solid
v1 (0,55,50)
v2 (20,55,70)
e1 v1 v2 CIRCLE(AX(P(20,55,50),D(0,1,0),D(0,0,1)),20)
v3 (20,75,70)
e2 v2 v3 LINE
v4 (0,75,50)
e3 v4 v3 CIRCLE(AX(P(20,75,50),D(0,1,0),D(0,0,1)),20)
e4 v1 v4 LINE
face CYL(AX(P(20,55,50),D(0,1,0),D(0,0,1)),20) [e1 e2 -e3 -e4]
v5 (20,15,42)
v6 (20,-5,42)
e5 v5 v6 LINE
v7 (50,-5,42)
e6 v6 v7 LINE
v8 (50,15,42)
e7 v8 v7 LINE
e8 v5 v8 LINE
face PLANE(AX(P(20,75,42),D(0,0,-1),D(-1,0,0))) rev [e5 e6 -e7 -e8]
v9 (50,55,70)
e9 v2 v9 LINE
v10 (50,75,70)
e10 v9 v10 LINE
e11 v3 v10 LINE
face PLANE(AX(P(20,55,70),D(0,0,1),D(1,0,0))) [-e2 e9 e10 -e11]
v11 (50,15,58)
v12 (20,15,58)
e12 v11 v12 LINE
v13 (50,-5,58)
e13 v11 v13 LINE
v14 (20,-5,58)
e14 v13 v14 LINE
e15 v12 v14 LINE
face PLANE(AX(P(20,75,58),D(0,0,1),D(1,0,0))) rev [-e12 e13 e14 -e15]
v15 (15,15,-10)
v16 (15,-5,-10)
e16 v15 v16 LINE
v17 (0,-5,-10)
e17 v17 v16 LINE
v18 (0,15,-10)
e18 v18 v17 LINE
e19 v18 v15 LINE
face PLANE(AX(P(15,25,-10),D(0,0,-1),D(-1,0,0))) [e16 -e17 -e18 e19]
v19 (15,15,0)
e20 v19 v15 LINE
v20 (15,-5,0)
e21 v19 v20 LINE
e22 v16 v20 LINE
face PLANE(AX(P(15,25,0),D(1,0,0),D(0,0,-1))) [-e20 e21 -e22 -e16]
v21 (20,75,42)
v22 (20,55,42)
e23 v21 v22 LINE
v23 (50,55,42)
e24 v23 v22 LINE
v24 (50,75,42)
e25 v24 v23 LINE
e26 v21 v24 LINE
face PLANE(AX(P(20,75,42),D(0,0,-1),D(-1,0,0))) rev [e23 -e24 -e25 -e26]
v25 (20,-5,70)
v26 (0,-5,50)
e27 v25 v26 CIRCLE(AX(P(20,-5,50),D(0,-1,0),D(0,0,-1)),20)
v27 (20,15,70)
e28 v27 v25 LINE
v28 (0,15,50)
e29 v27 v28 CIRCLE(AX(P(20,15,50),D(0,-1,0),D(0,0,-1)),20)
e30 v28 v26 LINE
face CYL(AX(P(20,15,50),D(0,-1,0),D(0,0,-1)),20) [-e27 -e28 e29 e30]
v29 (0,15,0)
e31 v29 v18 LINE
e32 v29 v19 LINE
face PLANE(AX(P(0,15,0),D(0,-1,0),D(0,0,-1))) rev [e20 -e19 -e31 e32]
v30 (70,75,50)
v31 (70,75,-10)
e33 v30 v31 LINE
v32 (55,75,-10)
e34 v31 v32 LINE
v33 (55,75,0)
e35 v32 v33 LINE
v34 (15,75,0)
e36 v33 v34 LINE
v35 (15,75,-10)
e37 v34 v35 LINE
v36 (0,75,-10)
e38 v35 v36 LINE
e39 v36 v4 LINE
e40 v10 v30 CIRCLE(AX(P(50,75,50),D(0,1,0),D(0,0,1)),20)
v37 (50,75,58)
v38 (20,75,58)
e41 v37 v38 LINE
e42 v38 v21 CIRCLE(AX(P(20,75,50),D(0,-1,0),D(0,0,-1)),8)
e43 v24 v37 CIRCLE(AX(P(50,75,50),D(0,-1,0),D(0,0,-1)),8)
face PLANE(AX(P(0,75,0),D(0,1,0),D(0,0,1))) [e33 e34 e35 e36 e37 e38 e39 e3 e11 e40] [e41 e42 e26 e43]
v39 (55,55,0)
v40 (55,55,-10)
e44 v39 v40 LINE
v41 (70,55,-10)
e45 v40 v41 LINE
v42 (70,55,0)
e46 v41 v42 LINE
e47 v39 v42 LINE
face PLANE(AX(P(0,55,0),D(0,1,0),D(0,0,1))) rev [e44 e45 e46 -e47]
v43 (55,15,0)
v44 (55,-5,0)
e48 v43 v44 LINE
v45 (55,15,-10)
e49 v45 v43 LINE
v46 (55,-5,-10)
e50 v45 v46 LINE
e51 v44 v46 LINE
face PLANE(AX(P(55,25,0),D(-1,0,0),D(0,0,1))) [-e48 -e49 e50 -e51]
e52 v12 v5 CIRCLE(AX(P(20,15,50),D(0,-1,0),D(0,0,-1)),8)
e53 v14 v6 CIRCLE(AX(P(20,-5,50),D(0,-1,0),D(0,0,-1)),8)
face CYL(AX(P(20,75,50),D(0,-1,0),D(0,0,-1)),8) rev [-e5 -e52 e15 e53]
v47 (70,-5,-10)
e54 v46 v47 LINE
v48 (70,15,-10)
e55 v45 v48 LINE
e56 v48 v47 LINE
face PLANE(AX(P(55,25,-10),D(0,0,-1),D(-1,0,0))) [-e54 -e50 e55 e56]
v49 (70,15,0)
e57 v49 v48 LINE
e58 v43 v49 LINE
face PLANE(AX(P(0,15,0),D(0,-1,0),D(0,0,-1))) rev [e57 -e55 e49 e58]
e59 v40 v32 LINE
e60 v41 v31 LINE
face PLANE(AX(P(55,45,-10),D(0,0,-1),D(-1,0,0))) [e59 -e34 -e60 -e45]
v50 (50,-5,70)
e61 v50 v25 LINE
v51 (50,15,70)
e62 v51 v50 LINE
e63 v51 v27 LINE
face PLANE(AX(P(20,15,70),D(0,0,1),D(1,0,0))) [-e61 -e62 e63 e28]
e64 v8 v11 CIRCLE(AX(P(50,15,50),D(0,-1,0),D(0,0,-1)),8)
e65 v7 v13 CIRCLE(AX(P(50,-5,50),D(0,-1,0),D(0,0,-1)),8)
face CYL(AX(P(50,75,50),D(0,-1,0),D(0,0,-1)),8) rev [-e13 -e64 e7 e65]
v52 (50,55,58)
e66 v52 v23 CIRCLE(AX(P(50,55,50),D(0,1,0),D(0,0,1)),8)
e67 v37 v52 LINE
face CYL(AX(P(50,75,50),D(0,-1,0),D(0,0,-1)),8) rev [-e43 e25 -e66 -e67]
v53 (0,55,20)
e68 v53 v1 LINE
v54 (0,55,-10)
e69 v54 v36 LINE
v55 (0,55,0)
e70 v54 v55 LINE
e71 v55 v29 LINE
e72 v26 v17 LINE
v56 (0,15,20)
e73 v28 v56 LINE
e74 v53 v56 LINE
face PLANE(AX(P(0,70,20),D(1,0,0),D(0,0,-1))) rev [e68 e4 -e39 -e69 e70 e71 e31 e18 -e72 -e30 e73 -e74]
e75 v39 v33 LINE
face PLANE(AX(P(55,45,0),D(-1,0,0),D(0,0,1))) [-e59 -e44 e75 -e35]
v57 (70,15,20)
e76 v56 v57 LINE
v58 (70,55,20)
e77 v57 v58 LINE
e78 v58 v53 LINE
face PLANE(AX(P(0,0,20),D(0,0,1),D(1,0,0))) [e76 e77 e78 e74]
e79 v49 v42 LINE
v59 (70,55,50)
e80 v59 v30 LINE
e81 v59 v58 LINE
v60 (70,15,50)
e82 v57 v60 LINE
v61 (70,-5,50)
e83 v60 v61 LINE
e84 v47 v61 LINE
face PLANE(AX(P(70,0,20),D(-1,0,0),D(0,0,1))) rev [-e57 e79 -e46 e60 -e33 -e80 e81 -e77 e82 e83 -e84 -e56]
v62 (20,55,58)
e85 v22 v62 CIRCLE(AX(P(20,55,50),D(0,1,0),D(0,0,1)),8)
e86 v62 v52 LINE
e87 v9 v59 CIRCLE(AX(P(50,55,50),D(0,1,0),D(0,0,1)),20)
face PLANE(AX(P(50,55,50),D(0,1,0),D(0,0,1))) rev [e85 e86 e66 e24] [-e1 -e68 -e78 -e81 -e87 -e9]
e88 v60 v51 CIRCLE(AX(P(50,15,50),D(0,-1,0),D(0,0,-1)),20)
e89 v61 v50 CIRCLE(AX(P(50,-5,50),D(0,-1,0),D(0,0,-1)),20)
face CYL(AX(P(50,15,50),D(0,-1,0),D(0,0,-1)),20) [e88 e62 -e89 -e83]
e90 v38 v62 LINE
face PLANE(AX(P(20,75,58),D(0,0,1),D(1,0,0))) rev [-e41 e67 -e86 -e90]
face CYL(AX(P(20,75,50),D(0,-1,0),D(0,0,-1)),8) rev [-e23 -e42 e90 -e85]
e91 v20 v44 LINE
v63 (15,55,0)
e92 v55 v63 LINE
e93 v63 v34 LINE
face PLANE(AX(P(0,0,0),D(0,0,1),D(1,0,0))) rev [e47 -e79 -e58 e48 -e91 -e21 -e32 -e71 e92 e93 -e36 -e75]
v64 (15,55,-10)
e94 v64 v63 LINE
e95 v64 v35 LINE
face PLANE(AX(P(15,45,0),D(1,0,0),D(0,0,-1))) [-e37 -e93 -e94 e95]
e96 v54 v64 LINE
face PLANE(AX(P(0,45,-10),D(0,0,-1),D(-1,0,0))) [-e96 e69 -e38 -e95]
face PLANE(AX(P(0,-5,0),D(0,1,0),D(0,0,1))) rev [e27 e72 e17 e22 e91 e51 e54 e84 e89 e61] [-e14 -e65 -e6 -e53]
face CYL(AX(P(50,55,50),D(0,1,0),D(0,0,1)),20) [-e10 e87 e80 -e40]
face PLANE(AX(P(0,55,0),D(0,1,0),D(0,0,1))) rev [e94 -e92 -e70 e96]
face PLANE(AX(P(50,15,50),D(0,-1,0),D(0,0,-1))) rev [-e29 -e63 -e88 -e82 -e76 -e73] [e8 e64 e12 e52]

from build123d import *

# Parameters (mm, degrees)
BASE_PLATE_SKETCH_W          = 70
BASE_PLATE_SKETCH_H          = 70
BASE_PLATE_70X70_DEPTH       = 20
WEB_BLOCK_SKETCH_W           = 15
WEB_BLOCK_SKETCH_H           = 10
WEB_BLOCK_DEPTH              = 25
SIDE_BLOCK_A_SKETCH_W        = 15
SIDE_BLOCK_A_SKETCH_H        = 10
SIDE_BLOCK_A_DEPTH           = 25
SIDE_BLOCK_B_SKETCH_W        = 15
SIDE_BLOCK_B_SKETCH_H        = 10
SIDE_BLOCK_B_DEPTH           = 25
POCKET_CUT_A_SKETCH_W        = 10
POCKET_CUT_A_SKETCH_H        = 10
POCKET_CUT_A_DEPTH           = 70
POCKET_CUT_B_SKETCH_W        = 10
POCKET_CUT_B_SKETCH_H        = 10
POCKET_CUT_B_DEPTH           = 70
FLANGE_A_5MM_DEPTH           = 5
FLANGE_B_5MM_DEPTH           = 5
ROUNDED_TAB_A_DEPTH          = 20
ROUNDED_START                = -20
ROUNDED_TAB_B_DEPTH          = 20
TAB_SLOTS_8X30_THROUGH_DEPTH = 80


with BuildPart() as part:
    # Base Plate Sketch → Base Plate 70x70 (new body)
    with BuildSketch(Plane.XY):
        with Locations((35, 35)):
            Rectangle(BASE_PLATE_SKETCH_W, BASE_PLATE_SKETCH_H)
    extrude(amount=BASE_PLATE_70X70_DEPTH)

    # Web Block Sketch → Web Block (add)
    with BuildSketch(Plane.XZ):
        with Locations((7.5, -5)):
            Rectangle(WEB_BLOCK_SKETCH_W, WEB_BLOCK_SKETCH_H)
        with Locations((62.5, -5)):
            Rectangle(WEB_BLOCK_SKETCH_W, WEB_BLOCK_SKETCH_H)
    extrude(amount=-WEB_BLOCK_DEPTH)

    # Side Block A Sketch → Side Block A (add)
    with BuildSketch(Plane(origin=(0, 70, 0), x_dir=(1, 0, 0), z_dir=(0, 1, 0))):
        with Locations((7.5, 5)):
            Rectangle(SIDE_BLOCK_A_SKETCH_W, SIDE_BLOCK_A_SKETCH_H)
    extrude(amount=-SIDE_BLOCK_A_DEPTH)

    # Side Block B Sketch → Side Block B (add)
    with BuildSketch(Plane(origin=(0, 70, 0), x_dir=(1, 0, 0), z_dir=(0, 1, 0))):
        with Locations((62.5, 5)):
            Rectangle(SIDE_BLOCK_B_SKETCH_W, SIDE_BLOCK_B_SKETCH_H)
    extrude(amount=-SIDE_BLOCK_B_DEPTH)

    # Pocket Cut A Sketch → Pocket Cut A (cut)
    with BuildSketch(Plane(origin=(70, 0, 0), x_dir=(0, 0, -1), z_dir=(1, 0, 0))):
        with Locations((5, 50)):
            Rectangle(POCKET_CUT_A_SKETCH_W, POCKET_CUT_A_SKETCH_H)
    extrude(amount=-POCKET_CUT_A_DEPTH, mode=Mode.SUBTRACT)

    # Pocket Cut B Sketch → Pocket Cut B (cut)
    with BuildSketch(Plane(origin=(70, 0, 0), x_dir=(0, 0, -1), z_dir=(1, 0, 0))):
        with Locations((5, 20)):
            Rectangle(POCKET_CUT_B_SKETCH_W, POCKET_CUT_B_SKETCH_H)
    extrude(amount=-POCKET_CUT_B_DEPTH, mode=Mode.SUBTRACT)

    # Flange A Sketch → Flange A 5mm (add)
    with BuildSketch(Plane.XZ):
        Polygon((0, 20), (70, 20), (70, -10), (55, -10), (55, 0), (15, 0), (15, -10), (0, -10), align=None)
    extrude(amount=FLANGE_A_5MM_DEPTH)

    # Flange B Sketch → Flange B 5mm (add)
    with BuildSketch(Plane(origin=(0, 70, 0), x_dir=(1, 0, 0), z_dir=(0, 1, 0))):
        Polygon((0, -20), (70, -20), (70, 10), (55, 10), (55, 0), (15, 0), (15, 10), (0, 10), align=None)
    extrude(amount=FLANGE_B_5MM_DEPTH)

    # Rounded Tab A Sketch → Rounded Tab A (add)
    with BuildSketch(Plane.XZ.offset(5)):
        with BuildLine():
            Line((0, 20), (0, 50))
            ThreePointArc((0, 50), (5.857864376, 64.142135624), (20, 70))
            Line((20, 70), (50, 70))
            ThreePointArc((50, 70), (64.142135624, 64.142135624), (70, 50))
            Line((70, 50), (70, 20))
            Line((70, 20), (0, 20))
        make_face()
    extrude(amount=-ROUNDED_TAB_A_DEPTH)

    # Rounded Tab B Sketch → Rounded Tab B (add)
    with BuildSketch(Plane(origin=(0, 75, 0), x_dir=(1, 0, 0), z_dir=(0, 1, 0)).offset(ROUNDED_START)):
        with BuildLine():
            Line((0, -20), (0, -50))
            ThreePointArc((0, -50), (5.857864376, -64.142135624), (20, -70))
            Line((20, -70), (50, -70))
            ThreePointArc((50, -70), (64.142135624, -64.142135624), (70, -50))
            Line((70, -50), (70, -20))
            Line((70, -20), (0, -20))
        make_face()
    extrude(amount=ROUNDED_TAB_B_DEPTH)

    # Tab Slots Sketch → Tab Slots 8x30 Through (cut)
    with BuildSketch(Plane.XZ.offset(5)):
        with BuildLine():
            Line((20, 58), (50, 58))
            ThreePointArc((50, 58), (58, 50), (50, 42))
            Line((50, 42), (20, 42))
            ThreePointArc((20, 42), (12, 50), (20, 58))
        make_face()
    extrude(amount=-TAB_SLOTS_8X30_THROUGH_DEPTH, mode=Mode.SUBTRACT)


solid = part.part
